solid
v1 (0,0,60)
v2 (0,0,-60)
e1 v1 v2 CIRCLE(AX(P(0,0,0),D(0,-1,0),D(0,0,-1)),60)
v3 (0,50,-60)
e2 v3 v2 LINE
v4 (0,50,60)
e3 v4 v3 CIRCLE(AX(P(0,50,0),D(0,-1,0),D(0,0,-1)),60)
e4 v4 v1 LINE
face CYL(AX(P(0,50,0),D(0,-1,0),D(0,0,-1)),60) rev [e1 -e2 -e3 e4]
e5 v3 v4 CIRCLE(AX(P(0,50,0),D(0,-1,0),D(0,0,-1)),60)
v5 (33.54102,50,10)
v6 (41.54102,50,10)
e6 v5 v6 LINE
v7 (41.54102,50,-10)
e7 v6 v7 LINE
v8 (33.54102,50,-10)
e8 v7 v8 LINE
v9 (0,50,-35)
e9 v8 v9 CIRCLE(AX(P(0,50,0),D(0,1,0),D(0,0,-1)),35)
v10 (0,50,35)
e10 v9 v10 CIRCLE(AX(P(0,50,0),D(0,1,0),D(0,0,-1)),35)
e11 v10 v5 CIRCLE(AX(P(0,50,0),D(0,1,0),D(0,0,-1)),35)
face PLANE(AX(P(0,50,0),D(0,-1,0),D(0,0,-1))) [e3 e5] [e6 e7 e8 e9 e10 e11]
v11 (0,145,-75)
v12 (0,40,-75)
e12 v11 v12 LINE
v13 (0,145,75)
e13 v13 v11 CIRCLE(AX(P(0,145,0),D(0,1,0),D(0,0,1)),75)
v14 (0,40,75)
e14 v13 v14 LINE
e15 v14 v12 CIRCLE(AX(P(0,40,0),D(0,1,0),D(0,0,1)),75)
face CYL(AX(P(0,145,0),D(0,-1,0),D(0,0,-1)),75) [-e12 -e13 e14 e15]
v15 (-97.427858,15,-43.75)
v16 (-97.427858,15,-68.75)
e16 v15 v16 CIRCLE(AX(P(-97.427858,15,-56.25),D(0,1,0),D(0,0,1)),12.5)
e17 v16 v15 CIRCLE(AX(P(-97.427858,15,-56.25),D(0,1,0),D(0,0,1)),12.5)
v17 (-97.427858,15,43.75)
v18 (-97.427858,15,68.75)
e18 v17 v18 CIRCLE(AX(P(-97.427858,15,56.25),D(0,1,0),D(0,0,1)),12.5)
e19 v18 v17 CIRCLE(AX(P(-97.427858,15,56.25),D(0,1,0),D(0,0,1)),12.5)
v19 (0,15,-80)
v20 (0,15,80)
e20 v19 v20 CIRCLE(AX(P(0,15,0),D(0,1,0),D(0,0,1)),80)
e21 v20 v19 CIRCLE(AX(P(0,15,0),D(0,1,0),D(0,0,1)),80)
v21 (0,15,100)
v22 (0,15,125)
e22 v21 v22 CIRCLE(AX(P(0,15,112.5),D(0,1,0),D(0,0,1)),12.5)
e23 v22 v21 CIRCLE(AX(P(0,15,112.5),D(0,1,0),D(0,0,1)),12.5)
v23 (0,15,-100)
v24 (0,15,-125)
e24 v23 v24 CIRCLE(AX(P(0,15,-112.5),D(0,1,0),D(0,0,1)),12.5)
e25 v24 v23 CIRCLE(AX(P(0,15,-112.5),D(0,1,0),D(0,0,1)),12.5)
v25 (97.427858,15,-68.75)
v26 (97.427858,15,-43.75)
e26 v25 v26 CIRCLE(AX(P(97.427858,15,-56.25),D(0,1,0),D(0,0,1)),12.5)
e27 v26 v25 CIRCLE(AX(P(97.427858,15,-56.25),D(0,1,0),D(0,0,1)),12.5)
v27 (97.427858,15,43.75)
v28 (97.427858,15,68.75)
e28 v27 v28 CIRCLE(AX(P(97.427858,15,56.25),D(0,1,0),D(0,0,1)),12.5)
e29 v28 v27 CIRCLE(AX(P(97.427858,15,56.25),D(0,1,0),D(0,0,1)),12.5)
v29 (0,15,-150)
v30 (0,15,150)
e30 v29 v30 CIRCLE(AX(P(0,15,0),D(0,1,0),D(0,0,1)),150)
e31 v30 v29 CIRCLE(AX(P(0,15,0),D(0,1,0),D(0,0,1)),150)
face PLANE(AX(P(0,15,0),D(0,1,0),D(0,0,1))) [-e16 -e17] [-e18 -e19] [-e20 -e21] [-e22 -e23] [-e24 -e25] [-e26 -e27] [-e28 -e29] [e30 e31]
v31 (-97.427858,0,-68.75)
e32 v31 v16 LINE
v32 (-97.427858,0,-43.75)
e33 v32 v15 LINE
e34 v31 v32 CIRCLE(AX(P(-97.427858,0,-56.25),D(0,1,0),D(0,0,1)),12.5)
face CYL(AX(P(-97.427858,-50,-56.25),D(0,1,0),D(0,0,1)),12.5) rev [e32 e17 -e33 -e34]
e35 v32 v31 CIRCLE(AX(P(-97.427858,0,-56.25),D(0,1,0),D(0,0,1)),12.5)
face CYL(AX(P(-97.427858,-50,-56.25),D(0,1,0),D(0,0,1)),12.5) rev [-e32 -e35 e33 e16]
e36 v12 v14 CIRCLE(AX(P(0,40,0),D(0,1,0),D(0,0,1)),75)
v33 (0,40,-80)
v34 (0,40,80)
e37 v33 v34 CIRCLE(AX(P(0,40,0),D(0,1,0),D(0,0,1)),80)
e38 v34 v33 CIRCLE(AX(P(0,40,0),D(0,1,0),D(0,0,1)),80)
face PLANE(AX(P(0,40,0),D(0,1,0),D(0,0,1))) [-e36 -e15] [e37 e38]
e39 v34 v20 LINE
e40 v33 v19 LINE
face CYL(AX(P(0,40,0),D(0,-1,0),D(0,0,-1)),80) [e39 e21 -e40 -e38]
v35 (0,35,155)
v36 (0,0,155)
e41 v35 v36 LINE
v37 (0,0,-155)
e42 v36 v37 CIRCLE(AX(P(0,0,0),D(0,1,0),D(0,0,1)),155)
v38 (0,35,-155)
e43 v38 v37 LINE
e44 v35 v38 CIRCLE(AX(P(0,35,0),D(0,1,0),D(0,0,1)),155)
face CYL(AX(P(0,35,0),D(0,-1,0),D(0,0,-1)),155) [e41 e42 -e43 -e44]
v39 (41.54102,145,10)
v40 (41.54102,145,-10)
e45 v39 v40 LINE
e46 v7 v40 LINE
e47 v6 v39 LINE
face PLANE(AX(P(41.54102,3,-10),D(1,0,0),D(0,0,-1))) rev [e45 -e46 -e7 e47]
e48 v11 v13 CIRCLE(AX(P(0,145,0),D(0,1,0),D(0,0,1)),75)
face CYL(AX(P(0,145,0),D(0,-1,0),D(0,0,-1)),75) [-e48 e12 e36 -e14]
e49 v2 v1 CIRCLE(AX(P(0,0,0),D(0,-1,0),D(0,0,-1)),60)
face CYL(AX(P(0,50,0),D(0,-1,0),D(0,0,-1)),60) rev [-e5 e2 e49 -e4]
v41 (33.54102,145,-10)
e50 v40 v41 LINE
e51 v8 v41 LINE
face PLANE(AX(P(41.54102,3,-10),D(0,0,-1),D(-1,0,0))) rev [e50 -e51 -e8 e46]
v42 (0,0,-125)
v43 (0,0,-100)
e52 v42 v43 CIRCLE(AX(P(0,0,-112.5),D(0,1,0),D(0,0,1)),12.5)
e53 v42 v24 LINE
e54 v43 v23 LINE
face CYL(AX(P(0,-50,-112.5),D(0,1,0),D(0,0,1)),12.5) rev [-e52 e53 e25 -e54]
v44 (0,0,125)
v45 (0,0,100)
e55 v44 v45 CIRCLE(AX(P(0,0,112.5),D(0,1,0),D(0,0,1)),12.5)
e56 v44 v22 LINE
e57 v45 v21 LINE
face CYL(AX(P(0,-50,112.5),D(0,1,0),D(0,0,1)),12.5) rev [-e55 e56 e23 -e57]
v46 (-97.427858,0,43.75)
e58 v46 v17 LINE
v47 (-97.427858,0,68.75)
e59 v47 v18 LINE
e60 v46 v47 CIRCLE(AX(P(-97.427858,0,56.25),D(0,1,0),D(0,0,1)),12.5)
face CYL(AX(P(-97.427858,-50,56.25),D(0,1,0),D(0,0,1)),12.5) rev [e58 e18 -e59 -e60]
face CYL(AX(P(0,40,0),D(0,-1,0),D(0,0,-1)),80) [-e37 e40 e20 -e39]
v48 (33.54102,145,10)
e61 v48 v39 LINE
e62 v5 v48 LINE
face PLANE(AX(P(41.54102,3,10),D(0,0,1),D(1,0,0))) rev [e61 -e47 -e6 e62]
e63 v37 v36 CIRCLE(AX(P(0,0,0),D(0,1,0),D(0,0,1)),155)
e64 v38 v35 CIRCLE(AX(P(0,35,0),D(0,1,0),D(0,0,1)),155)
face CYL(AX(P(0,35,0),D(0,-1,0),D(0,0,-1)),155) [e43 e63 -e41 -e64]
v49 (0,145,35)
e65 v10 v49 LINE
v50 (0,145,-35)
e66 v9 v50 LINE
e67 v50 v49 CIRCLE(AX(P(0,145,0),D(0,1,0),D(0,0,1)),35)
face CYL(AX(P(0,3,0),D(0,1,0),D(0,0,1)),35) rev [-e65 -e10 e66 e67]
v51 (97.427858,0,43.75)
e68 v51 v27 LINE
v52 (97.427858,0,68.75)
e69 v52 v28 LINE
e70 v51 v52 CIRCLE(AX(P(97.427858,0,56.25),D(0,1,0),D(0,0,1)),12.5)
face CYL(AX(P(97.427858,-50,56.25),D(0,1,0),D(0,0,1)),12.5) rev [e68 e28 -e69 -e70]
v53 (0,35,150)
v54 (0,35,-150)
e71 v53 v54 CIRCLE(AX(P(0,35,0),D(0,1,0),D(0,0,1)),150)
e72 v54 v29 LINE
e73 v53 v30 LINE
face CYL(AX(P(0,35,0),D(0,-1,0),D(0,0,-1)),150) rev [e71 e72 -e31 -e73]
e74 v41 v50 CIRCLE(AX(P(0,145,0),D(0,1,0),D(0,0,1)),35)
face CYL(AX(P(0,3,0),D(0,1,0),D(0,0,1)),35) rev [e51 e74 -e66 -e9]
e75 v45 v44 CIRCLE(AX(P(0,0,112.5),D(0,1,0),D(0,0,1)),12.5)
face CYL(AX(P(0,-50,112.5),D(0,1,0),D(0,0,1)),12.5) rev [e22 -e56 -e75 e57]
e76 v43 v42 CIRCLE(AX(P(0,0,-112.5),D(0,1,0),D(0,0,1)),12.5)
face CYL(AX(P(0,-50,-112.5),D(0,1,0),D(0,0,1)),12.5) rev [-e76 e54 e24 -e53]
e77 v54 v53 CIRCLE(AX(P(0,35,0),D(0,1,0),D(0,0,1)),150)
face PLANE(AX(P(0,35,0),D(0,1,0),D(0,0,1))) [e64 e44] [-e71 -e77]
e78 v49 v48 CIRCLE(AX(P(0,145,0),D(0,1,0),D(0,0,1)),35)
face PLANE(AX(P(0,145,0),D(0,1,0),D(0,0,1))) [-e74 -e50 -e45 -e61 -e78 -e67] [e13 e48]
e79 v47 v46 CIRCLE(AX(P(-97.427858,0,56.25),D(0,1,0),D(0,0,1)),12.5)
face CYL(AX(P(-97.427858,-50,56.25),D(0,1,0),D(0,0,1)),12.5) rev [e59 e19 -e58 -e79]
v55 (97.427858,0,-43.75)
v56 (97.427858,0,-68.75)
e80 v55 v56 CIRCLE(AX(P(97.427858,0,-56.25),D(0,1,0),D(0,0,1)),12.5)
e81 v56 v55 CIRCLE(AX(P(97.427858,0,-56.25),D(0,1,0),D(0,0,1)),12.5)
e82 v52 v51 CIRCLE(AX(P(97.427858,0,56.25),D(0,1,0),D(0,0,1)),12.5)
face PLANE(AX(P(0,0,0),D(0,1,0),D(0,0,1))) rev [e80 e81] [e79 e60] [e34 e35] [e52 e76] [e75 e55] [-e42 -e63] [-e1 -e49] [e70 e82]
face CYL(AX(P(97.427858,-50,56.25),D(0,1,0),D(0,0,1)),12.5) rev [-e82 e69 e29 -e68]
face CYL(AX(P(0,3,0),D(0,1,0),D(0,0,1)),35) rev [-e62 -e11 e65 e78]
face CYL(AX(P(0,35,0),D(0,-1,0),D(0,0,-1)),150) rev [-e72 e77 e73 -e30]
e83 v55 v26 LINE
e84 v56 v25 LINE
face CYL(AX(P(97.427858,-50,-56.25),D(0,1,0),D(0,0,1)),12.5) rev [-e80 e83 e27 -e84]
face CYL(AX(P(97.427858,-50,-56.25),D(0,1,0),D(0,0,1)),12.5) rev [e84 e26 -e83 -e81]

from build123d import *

# Parameters (mm, degrees)
FLANGE_RIM_SKETCH_R              = 155
FLANGE_RIM_SKETCH_R_2            = 150
FLANGE_RIM_310_DEPTH             = 35
FLANGE_BASE_SKETCH_R             = 150
FLANGE_BASE_DISC_DEPTH           = 15
MOUNTING_HOLES_SKETCH_R          = 12.5
MOUNTING_HOLES_6X_DEPTH          = 65
HUB_SHOULDER_SKETCH_R            = 80
HUB_SHOULDER_160_DEPTH           = 25
HUB_SKETCH_R                     = 75
HUB_150_DEPTH                    = 105
KEYED_BORE_WITH_KEYWAY_8X8_DEPTH = 142
RECESS_SKETCH_R                  = 60
RECESS_120_DEPTH                 = 50


with BuildPart() as part:
    # Flange Rim Sketch → Flange Rim Ø310 (new body)
    with BuildSketch(Plane(origin=(0, 0, 0), x_dir=(1, 0, 0), z_dir=(0, 1, 0))):
        with Locations(Location((0, 0, 0), (0, 0, 270))):
            Circle(FLANGE_RIM_SKETCH_R)
        with Locations(Location((0, 0, 0), (0, 0, 270))):
            Circle(FLANGE_RIM_SKETCH_R_2, mode=Mode.SUBTRACT)
    extrude(amount=FLANGE_RIM_310_DEPTH)

    # Flange Base Sketch → Flange Base Disc (add)
    with BuildSketch(Plane(origin=(0, 0, 0), x_dir=(1, 0, 0), z_dir=(0, 1, 0))):
        with Locations(Location((0, 0, 0), (0, 0, 270))):
            Circle(FLANGE_BASE_SKETCH_R)
    extrude(amount=FLANGE_BASE_DISC_DEPTH)

    # Mounting Holes Sketch → Mounting Holes 6x (cut)
    with BuildSketch(Plane(origin=(0, 15, 0), x_dir=(1, 0, 0), z_dir=(0, 1, 0))):
        with Locations(Location((0, 112.5, 0), (0, 0, 270))):
            Circle(MOUNTING_HOLES_SKETCH_R)
        with Locations(Location((97.427857926, 56.25, 0), (0, 0, 270))):
            Circle(MOUNTING_HOLES_SKETCH_R)
        with Locations(Location((97.427857926, -56.25, 0), (0, 0, 270))):
            Circle(MOUNTING_HOLES_SKETCH_R)
        with Locations(Location((0, -112.5, 0), (0, 0, 270))):
            Circle(MOUNTING_HOLES_SKETCH_R)
        with Locations(Location((-97.427857926, -56.25, 0), (0, 0, 270))):
            Circle(MOUNTING_HOLES_SKETCH_R)
        with Locations(Location((-97.427857926, 56.25, 0), (0, 0, 270))):
            Circle(MOUNTING_HOLES_SKETCH_R)
    extrude(amount=-MOUNTING_HOLES_6X_DEPTH, mode=Mode.SUBTRACT)

    # Hub Shoulder Sketch → Hub Shoulder Ø160 (add)
    with BuildSketch(Plane(origin=(0, 15, 0), x_dir=(1, 0, 0), z_dir=(0, 1, 0))):
        with Locations(Location((0, 0, 0), (0, 0, 270))):
            Circle(HUB_SHOULDER_SKETCH_R)
    extrude(amount=HUB_SHOULDER_160_DEPTH)

    # Hub Sketch → Hub Ø150 (add)
    with BuildSketch(Plane(origin=(0, 40, 0), x_dir=(1, 0, 0), z_dir=(0, 1, 0))):
        with Locations(Location((0, 0, 0), (0, 0, 270))):
            Circle(HUB_SKETCH_R)
    extrude(amount=HUB_150_DEPTH)

    # Keyed Bore Sketch → Keyed Bore with Keyway 8x8 (cut)
    with BuildSketch(Plane(origin=(0, 145, 0), x_dir=(1, 0, 0), z_dir=(0, 1, 0))):
        with BuildLine():
            Line((41.541019662, 10), (33.541019662, 10))
            ThreePointArc((33.541019662, 10), (-35, 0), (33.541019662, -10))
            Line((33.541019662, -10), (41.541019662, -10))
            Line((41.541019662, -10), (41.541019662, 10))
        make_face()
    extrude(amount=-KEYED_BORE_WITH_KEYWAY_8X8_DEPTH, mode=Mode.SUBTRACT)

    # Recess Sketch → Recess Ø120 (cut)
    with BuildSketch(Plane.XZ):
        with Locations(Location((0, 0, 0), (0, 0, 270))):
            Circle(RECESS_SKETCH_R)
    extrude(amount=-RECESS_120_DEPTH, mode=Mode.SUBTRACT)


solid = part.part
